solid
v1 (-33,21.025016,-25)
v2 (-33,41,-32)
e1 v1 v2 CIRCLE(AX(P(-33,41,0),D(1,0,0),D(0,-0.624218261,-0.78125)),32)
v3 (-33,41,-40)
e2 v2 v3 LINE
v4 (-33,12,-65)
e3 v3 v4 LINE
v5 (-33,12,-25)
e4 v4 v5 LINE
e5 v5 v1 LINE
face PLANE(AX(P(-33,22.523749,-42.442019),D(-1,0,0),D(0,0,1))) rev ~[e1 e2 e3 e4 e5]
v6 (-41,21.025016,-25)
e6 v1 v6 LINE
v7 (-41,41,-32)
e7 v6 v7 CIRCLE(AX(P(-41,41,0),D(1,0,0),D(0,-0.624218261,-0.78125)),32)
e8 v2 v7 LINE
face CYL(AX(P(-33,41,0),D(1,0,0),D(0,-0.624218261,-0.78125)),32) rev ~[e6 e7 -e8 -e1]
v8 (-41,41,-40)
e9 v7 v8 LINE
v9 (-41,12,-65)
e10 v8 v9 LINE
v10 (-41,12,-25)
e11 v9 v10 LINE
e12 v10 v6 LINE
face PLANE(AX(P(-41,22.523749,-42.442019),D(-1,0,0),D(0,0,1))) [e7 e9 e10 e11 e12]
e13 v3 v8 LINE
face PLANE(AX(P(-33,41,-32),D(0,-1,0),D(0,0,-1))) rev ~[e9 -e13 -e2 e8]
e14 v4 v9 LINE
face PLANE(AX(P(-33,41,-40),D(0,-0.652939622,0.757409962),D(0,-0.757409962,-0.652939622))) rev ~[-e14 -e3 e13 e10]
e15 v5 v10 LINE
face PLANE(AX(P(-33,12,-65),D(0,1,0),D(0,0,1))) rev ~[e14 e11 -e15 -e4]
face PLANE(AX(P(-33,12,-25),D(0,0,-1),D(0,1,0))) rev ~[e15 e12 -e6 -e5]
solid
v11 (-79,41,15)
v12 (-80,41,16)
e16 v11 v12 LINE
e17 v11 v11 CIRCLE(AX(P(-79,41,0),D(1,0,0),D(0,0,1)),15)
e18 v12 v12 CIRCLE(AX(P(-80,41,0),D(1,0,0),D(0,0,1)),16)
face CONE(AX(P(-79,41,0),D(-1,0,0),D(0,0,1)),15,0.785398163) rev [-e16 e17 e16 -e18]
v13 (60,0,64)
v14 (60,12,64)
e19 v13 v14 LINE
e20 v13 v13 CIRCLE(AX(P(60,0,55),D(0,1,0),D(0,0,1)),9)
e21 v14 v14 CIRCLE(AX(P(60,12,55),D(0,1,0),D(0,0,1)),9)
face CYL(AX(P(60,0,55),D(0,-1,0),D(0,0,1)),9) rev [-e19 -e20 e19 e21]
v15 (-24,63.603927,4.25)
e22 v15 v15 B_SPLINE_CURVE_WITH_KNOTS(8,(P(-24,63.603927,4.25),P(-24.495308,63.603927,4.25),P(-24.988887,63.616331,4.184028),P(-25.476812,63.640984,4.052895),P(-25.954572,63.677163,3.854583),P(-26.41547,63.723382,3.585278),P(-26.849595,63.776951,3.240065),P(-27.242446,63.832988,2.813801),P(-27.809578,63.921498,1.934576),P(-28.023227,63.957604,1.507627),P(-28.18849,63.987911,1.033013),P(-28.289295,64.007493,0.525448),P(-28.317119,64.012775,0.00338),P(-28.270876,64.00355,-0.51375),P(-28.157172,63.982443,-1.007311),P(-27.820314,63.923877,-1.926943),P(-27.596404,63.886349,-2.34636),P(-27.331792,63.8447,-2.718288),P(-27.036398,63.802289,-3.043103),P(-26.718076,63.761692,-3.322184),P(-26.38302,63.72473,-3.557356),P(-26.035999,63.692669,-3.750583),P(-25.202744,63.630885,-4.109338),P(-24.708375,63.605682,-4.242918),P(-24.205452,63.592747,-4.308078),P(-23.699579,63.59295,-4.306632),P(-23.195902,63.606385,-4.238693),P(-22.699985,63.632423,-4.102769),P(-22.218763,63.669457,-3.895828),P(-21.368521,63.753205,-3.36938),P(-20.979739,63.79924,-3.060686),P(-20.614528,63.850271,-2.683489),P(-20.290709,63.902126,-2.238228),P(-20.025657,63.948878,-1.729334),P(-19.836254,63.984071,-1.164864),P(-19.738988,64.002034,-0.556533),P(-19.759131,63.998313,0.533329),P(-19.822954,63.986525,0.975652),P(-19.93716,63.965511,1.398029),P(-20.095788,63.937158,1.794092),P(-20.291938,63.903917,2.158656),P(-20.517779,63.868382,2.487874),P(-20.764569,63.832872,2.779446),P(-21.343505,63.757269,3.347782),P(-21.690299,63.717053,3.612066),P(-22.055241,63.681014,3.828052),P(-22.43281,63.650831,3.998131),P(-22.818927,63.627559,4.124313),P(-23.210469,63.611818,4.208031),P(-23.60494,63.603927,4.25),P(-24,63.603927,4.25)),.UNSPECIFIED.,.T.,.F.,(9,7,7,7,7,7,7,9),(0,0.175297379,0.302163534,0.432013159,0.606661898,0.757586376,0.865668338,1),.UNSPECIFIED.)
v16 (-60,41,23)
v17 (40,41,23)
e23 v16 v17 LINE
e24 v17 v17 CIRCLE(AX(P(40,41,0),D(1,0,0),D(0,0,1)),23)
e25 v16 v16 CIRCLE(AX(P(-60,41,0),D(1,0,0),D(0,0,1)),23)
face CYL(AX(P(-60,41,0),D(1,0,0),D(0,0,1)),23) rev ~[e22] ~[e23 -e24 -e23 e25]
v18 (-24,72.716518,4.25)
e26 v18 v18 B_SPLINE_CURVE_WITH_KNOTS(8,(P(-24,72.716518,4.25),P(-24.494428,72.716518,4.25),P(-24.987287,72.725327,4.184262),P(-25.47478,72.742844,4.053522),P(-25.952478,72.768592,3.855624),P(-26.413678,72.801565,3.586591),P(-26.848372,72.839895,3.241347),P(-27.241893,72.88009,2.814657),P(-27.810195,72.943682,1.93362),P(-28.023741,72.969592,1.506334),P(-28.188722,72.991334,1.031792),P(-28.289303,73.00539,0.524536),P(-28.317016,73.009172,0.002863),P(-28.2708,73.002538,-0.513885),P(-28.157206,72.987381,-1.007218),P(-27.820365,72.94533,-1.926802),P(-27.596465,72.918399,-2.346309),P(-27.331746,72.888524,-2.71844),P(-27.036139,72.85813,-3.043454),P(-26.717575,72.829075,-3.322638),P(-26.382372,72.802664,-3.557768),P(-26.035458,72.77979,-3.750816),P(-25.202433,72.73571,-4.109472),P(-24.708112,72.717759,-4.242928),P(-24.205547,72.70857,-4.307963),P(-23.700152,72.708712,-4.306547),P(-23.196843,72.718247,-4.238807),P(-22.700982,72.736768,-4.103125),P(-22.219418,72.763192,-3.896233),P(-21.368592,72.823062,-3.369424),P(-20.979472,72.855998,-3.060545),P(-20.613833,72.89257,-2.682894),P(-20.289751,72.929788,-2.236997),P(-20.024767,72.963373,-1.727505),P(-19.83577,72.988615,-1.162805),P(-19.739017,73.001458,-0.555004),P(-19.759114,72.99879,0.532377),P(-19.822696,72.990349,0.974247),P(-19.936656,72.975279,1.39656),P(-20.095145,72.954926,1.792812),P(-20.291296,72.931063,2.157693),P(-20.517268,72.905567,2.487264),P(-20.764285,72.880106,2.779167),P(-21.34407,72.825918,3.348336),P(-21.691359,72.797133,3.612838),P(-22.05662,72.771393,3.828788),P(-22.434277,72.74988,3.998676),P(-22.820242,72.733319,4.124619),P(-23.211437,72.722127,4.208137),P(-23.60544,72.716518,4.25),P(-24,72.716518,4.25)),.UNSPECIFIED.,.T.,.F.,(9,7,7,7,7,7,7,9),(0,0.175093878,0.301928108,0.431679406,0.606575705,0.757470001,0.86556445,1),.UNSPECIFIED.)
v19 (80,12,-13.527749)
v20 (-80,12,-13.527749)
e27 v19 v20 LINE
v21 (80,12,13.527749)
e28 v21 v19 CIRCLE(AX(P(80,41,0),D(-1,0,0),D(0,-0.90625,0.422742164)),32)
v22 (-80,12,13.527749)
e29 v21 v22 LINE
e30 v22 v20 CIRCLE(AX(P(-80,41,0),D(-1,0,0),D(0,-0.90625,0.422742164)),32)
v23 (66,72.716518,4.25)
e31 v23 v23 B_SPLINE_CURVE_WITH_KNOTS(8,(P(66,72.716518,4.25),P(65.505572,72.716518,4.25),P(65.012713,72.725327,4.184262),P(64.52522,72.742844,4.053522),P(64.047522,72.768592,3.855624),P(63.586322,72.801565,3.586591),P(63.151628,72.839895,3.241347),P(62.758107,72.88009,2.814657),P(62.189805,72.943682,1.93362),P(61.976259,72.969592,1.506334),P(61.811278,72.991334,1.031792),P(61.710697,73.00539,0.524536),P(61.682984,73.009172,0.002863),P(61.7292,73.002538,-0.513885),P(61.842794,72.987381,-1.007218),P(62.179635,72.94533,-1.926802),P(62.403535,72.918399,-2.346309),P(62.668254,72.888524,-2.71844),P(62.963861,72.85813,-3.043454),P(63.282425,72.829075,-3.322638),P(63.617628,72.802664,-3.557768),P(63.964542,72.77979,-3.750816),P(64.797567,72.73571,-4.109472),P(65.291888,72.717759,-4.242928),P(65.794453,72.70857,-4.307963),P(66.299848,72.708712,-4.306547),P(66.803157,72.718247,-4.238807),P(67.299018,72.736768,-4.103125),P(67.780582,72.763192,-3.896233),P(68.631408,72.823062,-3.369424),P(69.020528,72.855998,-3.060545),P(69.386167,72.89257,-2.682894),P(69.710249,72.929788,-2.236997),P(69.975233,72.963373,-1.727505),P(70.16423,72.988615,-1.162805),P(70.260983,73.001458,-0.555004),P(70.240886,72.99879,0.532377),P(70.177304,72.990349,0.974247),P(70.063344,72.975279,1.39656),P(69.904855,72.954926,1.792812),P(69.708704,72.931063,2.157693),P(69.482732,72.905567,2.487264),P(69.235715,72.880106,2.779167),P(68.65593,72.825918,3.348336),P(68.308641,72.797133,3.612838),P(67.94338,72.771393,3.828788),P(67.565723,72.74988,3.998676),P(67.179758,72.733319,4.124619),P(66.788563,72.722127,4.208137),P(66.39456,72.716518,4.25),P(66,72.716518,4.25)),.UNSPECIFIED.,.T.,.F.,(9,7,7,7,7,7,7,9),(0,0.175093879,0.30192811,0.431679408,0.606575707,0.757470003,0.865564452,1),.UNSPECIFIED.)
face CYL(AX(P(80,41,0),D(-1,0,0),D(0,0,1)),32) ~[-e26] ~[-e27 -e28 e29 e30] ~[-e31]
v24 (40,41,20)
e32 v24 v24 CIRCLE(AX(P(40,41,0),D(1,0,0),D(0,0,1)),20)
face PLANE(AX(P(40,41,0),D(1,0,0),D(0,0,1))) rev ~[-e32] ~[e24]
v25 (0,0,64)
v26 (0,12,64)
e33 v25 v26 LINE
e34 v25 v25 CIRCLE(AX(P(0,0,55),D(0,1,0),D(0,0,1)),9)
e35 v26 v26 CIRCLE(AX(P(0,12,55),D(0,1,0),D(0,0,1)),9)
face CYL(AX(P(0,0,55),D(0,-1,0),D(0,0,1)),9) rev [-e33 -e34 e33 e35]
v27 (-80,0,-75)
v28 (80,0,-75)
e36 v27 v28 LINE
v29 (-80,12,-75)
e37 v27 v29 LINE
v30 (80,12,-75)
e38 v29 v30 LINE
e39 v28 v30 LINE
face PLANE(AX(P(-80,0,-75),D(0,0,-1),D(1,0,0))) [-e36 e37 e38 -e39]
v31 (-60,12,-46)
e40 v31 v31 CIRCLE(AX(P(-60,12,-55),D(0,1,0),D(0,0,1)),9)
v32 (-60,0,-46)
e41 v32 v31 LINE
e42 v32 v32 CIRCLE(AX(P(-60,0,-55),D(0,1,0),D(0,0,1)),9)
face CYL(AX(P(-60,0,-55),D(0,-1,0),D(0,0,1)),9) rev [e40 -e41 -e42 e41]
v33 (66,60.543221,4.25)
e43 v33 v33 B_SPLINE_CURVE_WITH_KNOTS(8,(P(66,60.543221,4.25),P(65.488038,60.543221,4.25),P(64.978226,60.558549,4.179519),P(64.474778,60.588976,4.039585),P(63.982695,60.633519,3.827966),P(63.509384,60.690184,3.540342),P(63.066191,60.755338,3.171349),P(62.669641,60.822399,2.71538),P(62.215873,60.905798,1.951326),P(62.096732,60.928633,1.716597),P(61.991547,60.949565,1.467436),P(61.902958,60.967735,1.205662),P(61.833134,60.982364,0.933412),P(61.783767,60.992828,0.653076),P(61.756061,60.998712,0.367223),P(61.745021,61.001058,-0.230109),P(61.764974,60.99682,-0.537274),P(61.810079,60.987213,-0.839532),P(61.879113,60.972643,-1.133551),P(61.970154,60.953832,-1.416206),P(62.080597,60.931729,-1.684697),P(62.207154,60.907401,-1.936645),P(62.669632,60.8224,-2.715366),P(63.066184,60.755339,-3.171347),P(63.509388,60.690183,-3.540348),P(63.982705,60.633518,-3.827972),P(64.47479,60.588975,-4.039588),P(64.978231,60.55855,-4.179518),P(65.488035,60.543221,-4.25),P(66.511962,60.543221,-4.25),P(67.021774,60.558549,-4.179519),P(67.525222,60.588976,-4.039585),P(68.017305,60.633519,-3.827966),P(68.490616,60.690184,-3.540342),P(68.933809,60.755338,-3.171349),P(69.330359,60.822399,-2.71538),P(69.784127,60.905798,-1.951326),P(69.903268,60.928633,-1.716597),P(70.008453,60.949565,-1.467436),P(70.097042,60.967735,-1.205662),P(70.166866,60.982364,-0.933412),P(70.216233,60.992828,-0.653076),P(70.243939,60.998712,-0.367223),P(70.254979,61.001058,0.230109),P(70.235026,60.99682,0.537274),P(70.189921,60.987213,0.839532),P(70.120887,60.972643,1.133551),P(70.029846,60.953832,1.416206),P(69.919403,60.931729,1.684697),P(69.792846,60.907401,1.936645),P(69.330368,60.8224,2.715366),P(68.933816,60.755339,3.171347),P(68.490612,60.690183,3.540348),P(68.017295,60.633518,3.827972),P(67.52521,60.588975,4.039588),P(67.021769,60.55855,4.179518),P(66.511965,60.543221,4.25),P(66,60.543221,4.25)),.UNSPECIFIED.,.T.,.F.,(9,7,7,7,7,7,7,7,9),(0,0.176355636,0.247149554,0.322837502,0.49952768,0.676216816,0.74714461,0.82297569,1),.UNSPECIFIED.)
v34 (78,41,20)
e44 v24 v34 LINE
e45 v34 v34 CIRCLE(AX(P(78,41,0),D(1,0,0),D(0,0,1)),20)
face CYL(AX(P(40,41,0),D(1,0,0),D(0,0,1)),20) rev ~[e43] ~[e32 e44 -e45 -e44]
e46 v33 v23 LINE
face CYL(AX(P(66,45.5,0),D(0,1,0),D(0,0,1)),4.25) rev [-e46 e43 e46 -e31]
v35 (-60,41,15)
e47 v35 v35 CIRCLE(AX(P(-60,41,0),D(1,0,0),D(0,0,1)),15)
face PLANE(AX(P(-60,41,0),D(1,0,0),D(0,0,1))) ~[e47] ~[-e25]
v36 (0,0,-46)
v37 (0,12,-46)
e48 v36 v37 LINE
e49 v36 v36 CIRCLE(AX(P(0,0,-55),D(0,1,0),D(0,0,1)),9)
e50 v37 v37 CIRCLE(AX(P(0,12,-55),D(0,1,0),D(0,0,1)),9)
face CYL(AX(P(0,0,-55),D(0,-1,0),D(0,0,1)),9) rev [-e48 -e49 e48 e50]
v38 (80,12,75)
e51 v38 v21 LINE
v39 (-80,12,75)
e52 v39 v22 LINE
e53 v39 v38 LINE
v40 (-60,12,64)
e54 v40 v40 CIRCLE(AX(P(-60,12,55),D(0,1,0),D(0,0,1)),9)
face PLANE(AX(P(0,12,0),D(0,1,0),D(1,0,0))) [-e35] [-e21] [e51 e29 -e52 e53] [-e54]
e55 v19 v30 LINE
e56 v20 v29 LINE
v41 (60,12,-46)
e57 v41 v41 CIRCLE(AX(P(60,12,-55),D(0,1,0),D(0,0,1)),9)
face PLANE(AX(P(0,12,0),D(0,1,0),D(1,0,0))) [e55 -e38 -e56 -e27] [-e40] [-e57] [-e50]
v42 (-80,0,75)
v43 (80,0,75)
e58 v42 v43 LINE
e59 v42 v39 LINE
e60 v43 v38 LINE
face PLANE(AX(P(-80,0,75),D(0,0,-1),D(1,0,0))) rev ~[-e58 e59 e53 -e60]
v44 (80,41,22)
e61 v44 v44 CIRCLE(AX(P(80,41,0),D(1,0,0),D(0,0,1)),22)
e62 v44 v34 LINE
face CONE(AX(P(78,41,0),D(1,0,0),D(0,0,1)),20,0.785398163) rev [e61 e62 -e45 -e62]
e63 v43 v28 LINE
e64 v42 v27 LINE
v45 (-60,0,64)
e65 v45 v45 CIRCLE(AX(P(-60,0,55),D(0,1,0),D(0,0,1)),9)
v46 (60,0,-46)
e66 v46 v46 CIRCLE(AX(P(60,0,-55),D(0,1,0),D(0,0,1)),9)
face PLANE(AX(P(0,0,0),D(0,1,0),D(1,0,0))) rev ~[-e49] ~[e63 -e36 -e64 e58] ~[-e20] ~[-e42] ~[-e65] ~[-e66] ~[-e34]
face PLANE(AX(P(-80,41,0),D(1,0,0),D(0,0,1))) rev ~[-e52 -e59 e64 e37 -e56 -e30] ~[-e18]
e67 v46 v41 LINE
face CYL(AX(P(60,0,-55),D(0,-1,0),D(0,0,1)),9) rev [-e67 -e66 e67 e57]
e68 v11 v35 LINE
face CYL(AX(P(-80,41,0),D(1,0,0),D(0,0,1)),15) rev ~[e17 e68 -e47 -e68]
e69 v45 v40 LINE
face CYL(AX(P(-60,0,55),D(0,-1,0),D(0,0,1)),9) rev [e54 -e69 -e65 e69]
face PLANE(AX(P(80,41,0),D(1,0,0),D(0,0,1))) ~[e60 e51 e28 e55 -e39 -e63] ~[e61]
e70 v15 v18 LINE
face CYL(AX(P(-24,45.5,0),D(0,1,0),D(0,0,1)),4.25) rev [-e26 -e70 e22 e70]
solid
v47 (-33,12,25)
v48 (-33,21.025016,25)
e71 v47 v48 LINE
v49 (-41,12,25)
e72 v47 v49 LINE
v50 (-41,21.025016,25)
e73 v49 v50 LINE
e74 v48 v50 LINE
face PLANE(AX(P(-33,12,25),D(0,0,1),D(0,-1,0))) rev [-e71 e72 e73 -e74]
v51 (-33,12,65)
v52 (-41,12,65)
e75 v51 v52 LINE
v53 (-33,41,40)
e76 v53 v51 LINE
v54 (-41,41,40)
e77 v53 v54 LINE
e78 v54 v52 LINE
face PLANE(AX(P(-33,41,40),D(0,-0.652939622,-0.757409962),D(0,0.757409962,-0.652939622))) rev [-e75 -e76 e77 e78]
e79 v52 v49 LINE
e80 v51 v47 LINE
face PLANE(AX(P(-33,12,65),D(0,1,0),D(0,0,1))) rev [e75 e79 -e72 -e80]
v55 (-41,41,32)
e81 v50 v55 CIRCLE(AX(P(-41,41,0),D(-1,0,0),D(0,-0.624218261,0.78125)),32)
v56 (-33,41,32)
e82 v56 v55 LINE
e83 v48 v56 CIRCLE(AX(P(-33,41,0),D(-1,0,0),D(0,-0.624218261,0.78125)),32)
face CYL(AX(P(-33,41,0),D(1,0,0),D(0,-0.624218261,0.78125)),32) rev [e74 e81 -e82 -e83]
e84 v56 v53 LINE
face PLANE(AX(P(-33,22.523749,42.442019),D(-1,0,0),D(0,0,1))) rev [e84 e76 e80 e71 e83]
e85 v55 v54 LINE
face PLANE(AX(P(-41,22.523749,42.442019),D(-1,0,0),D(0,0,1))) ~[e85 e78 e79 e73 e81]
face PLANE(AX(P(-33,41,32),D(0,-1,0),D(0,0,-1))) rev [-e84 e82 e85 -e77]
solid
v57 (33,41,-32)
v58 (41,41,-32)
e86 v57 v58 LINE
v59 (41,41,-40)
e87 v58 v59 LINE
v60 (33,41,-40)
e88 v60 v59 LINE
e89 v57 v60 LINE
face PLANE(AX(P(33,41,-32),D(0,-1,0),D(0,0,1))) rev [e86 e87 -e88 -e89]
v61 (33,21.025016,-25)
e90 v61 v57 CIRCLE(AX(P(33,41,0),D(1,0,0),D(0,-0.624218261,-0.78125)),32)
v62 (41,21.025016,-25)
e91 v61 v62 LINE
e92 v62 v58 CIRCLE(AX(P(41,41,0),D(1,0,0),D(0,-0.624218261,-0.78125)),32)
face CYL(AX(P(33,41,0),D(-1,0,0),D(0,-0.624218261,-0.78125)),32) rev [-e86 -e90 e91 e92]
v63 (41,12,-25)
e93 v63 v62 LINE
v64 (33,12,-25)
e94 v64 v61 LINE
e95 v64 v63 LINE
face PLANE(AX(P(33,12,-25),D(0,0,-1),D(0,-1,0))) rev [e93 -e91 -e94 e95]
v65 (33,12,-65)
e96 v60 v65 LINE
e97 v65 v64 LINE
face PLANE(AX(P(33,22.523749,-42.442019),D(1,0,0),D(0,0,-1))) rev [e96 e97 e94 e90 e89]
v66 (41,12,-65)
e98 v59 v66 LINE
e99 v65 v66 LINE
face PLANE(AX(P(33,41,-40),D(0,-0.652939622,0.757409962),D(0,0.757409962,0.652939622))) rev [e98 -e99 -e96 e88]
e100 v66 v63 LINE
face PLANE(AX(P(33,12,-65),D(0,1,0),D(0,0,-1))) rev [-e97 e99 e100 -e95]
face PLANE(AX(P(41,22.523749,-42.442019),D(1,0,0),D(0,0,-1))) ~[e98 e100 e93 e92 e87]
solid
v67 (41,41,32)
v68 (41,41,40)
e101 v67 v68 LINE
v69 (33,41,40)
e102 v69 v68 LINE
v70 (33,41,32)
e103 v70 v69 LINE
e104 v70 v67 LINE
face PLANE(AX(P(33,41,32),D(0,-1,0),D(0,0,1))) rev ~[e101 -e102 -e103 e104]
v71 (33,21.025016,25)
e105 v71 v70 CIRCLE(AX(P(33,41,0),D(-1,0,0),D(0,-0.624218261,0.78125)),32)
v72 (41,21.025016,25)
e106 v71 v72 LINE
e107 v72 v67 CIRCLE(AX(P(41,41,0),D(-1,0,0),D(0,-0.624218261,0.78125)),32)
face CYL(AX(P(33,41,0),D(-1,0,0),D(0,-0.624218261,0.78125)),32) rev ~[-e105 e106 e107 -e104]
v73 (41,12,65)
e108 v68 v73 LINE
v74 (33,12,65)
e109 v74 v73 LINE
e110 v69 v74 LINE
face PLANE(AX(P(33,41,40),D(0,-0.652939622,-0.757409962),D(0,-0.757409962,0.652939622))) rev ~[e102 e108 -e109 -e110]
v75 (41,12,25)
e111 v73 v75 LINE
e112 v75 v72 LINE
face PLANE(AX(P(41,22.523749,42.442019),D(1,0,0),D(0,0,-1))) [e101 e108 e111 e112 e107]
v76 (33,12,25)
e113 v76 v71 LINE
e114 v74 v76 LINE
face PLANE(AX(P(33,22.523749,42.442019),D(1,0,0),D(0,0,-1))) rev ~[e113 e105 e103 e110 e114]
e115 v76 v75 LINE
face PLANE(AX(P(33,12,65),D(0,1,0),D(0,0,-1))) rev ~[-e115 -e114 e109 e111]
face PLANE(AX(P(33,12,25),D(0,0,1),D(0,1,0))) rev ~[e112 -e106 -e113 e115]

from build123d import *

# Parameters (mm, degrees)
SKETCH_1_W                   = 160
SKETCH_1_H                   = 150
SKETCH_1_R                   = 9
EXTRUDE_1_DEPTH              = 12
EXTRUDE_START                = 33
EXTRUDE_2_DEPTH              = 8
HOLE_WIZARD_M10_1_AT_2_COUNT = 2
HOLE_WIZARD_M10_1_AT_2_PITCH = 90
CHAMFER_1_SIZE               = 1
CHAMFER_2_SIZE               = 2


with BuildPart() as part:
    # 草图1 → 凸台-拉伸1 (new body)
    with BuildSketch(Plane(origin=(0, 0, 0), x_dir=(1, 0, 0), z_dir=(0, 1, 0))):
        Rectangle(SKETCH_1_W, SKETCH_1_H)
        with Locations(Location((-60, -55, 0), (0, 0, 270))):
            Circle(SKETCH_1_R, mode=Mode.SUBTRACT)
        with Locations(Location((0, -55, 0), (0, 0, 270))):
            Circle(SKETCH_1_R, mode=Mode.SUBTRACT)
        with Locations(Location((60, -55, 0), (0, 0, 270))):
            Circle(SKETCH_1_R, mode=Mode.SUBTRACT)
        with Locations(Location((0, 55, 0), (0, 0, 270))):
            Circle(SKETCH_1_R, mode=Mode.SUBTRACT)
        with Locations(Location((60, 55, 0), (0, 0, 270))):
            Circle(SKETCH_1_R, mode=Mode.SUBTRACT)
        with Locations(Location((-60, 55, 0), (0, 0, 270))):
            Circle(SKETCH_1_R, mode=Mode.SUBTRACT)
    extrude(amount=EXTRUDE_1_DEPTH)

    # 草图2 → 旋转1 (revolve)
    with BuildSketch(Plane.XY, mode=Mode.PRIVATE) as revolve_1_sk:
        Polygon((-80, 56), (-60, 56), (-60, 64), (40, 64), (40, 61), (80, 61), (80, 73), (-80, 73), align=None)
    revolve(revolve_1_sk.sketch.rotate(Axis((-77.946721126, 41, 0), (1, 0, 0)), 90), axis=Axis((-77.946721126, 41, 0), (1, 0, 0)))

    # 草图6 → M10 螺纹孔1 (revolve, cut)
    with BuildSketch(Plane(origin=(-24, 73, 0), x_dir=(0, 0, 1), z_dir=(1, 0, 0))):
        Polygon((0, 0), (0, 30.053657631), (4.25, 27.5), (4.25, 0), align=None)
    hole_wizard_m10_1 = revolve(axis=Axis((-24, 79.35, 0), (0, -1, 0)), mode=Mode.SUBTRACT)

    # M10 螺纹孔1 at 2: M10 螺纹孔1 ×2
    with Locations(*[(i * HOLE_WIZARD_M10_1_AT_2_PITCH, 0, 0) for i in range(1, HOLE_WIZARD_M10_1_AT_2_COUNT)]):
        add(hole_wizard_m10_1, mode=Mode.SUBTRACT)

    # 倒角1
    chamfer_1_edges = [part.edges().sort_by_distance(p)[0] for p in [
        (-80, 41, -15),
    ]]
    chamfer(chamfer_1_edges, length=CHAMFER_1_SIZE)

    # 倒角2
    chamfer_2_edges = [part.edges().sort_by_distance(p)[0] for p in [
        (80, 41, -20),
    ]]
    chamfer(chamfer_2_edges, length=CHAMFER_2_SIZE)


with BuildPart() as body_2:
    # 草图4 → 凸台-拉伸2 (new body)
    with BuildSketch(Plane(origin=(0, 0, 0), x_dir=(0, 0, -1), z_dir=(1, 0, 0)).offset(EXTRUDE_START)):
        with BuildLine():
            Line((-32, 41), (-40, 41))
            Line((-40, 41), (-65, 12))
            Line((-65, 12), (-25, 12))
            Line((-25, 12), (-25, 21.025015645))
            ThreePointArc((-25, 21.025015645), (-30.199337741, 30.416994756), (-32, 41))
        make_face()
    extrude(amount=EXTRUDE_2_DEPTH)


with BuildPart() as body_3:
    # 镜向1: mirrored copy
    add(body_2.part.mirror(Plane.XY))


with BuildPart() as body_4:
    # 镜向2: mirrored copy
    add(body_3.part.mirror(Plane(origin=(0, 0, 0), x_dir=(0, 0, 1), z_dir=(1, 0, 0))))


with BuildPart() as body_5:
    # Mirror 2 2: mirrored copy
    add(body_2.part.mirror(Plane(origin=(0, 0, 0), x_dir=(0, 0, 1), z_dir=(1, 0, 0))))


solid = Compound([part.part, body_2.part, body_3.part, body_4.part, body_5.part])
